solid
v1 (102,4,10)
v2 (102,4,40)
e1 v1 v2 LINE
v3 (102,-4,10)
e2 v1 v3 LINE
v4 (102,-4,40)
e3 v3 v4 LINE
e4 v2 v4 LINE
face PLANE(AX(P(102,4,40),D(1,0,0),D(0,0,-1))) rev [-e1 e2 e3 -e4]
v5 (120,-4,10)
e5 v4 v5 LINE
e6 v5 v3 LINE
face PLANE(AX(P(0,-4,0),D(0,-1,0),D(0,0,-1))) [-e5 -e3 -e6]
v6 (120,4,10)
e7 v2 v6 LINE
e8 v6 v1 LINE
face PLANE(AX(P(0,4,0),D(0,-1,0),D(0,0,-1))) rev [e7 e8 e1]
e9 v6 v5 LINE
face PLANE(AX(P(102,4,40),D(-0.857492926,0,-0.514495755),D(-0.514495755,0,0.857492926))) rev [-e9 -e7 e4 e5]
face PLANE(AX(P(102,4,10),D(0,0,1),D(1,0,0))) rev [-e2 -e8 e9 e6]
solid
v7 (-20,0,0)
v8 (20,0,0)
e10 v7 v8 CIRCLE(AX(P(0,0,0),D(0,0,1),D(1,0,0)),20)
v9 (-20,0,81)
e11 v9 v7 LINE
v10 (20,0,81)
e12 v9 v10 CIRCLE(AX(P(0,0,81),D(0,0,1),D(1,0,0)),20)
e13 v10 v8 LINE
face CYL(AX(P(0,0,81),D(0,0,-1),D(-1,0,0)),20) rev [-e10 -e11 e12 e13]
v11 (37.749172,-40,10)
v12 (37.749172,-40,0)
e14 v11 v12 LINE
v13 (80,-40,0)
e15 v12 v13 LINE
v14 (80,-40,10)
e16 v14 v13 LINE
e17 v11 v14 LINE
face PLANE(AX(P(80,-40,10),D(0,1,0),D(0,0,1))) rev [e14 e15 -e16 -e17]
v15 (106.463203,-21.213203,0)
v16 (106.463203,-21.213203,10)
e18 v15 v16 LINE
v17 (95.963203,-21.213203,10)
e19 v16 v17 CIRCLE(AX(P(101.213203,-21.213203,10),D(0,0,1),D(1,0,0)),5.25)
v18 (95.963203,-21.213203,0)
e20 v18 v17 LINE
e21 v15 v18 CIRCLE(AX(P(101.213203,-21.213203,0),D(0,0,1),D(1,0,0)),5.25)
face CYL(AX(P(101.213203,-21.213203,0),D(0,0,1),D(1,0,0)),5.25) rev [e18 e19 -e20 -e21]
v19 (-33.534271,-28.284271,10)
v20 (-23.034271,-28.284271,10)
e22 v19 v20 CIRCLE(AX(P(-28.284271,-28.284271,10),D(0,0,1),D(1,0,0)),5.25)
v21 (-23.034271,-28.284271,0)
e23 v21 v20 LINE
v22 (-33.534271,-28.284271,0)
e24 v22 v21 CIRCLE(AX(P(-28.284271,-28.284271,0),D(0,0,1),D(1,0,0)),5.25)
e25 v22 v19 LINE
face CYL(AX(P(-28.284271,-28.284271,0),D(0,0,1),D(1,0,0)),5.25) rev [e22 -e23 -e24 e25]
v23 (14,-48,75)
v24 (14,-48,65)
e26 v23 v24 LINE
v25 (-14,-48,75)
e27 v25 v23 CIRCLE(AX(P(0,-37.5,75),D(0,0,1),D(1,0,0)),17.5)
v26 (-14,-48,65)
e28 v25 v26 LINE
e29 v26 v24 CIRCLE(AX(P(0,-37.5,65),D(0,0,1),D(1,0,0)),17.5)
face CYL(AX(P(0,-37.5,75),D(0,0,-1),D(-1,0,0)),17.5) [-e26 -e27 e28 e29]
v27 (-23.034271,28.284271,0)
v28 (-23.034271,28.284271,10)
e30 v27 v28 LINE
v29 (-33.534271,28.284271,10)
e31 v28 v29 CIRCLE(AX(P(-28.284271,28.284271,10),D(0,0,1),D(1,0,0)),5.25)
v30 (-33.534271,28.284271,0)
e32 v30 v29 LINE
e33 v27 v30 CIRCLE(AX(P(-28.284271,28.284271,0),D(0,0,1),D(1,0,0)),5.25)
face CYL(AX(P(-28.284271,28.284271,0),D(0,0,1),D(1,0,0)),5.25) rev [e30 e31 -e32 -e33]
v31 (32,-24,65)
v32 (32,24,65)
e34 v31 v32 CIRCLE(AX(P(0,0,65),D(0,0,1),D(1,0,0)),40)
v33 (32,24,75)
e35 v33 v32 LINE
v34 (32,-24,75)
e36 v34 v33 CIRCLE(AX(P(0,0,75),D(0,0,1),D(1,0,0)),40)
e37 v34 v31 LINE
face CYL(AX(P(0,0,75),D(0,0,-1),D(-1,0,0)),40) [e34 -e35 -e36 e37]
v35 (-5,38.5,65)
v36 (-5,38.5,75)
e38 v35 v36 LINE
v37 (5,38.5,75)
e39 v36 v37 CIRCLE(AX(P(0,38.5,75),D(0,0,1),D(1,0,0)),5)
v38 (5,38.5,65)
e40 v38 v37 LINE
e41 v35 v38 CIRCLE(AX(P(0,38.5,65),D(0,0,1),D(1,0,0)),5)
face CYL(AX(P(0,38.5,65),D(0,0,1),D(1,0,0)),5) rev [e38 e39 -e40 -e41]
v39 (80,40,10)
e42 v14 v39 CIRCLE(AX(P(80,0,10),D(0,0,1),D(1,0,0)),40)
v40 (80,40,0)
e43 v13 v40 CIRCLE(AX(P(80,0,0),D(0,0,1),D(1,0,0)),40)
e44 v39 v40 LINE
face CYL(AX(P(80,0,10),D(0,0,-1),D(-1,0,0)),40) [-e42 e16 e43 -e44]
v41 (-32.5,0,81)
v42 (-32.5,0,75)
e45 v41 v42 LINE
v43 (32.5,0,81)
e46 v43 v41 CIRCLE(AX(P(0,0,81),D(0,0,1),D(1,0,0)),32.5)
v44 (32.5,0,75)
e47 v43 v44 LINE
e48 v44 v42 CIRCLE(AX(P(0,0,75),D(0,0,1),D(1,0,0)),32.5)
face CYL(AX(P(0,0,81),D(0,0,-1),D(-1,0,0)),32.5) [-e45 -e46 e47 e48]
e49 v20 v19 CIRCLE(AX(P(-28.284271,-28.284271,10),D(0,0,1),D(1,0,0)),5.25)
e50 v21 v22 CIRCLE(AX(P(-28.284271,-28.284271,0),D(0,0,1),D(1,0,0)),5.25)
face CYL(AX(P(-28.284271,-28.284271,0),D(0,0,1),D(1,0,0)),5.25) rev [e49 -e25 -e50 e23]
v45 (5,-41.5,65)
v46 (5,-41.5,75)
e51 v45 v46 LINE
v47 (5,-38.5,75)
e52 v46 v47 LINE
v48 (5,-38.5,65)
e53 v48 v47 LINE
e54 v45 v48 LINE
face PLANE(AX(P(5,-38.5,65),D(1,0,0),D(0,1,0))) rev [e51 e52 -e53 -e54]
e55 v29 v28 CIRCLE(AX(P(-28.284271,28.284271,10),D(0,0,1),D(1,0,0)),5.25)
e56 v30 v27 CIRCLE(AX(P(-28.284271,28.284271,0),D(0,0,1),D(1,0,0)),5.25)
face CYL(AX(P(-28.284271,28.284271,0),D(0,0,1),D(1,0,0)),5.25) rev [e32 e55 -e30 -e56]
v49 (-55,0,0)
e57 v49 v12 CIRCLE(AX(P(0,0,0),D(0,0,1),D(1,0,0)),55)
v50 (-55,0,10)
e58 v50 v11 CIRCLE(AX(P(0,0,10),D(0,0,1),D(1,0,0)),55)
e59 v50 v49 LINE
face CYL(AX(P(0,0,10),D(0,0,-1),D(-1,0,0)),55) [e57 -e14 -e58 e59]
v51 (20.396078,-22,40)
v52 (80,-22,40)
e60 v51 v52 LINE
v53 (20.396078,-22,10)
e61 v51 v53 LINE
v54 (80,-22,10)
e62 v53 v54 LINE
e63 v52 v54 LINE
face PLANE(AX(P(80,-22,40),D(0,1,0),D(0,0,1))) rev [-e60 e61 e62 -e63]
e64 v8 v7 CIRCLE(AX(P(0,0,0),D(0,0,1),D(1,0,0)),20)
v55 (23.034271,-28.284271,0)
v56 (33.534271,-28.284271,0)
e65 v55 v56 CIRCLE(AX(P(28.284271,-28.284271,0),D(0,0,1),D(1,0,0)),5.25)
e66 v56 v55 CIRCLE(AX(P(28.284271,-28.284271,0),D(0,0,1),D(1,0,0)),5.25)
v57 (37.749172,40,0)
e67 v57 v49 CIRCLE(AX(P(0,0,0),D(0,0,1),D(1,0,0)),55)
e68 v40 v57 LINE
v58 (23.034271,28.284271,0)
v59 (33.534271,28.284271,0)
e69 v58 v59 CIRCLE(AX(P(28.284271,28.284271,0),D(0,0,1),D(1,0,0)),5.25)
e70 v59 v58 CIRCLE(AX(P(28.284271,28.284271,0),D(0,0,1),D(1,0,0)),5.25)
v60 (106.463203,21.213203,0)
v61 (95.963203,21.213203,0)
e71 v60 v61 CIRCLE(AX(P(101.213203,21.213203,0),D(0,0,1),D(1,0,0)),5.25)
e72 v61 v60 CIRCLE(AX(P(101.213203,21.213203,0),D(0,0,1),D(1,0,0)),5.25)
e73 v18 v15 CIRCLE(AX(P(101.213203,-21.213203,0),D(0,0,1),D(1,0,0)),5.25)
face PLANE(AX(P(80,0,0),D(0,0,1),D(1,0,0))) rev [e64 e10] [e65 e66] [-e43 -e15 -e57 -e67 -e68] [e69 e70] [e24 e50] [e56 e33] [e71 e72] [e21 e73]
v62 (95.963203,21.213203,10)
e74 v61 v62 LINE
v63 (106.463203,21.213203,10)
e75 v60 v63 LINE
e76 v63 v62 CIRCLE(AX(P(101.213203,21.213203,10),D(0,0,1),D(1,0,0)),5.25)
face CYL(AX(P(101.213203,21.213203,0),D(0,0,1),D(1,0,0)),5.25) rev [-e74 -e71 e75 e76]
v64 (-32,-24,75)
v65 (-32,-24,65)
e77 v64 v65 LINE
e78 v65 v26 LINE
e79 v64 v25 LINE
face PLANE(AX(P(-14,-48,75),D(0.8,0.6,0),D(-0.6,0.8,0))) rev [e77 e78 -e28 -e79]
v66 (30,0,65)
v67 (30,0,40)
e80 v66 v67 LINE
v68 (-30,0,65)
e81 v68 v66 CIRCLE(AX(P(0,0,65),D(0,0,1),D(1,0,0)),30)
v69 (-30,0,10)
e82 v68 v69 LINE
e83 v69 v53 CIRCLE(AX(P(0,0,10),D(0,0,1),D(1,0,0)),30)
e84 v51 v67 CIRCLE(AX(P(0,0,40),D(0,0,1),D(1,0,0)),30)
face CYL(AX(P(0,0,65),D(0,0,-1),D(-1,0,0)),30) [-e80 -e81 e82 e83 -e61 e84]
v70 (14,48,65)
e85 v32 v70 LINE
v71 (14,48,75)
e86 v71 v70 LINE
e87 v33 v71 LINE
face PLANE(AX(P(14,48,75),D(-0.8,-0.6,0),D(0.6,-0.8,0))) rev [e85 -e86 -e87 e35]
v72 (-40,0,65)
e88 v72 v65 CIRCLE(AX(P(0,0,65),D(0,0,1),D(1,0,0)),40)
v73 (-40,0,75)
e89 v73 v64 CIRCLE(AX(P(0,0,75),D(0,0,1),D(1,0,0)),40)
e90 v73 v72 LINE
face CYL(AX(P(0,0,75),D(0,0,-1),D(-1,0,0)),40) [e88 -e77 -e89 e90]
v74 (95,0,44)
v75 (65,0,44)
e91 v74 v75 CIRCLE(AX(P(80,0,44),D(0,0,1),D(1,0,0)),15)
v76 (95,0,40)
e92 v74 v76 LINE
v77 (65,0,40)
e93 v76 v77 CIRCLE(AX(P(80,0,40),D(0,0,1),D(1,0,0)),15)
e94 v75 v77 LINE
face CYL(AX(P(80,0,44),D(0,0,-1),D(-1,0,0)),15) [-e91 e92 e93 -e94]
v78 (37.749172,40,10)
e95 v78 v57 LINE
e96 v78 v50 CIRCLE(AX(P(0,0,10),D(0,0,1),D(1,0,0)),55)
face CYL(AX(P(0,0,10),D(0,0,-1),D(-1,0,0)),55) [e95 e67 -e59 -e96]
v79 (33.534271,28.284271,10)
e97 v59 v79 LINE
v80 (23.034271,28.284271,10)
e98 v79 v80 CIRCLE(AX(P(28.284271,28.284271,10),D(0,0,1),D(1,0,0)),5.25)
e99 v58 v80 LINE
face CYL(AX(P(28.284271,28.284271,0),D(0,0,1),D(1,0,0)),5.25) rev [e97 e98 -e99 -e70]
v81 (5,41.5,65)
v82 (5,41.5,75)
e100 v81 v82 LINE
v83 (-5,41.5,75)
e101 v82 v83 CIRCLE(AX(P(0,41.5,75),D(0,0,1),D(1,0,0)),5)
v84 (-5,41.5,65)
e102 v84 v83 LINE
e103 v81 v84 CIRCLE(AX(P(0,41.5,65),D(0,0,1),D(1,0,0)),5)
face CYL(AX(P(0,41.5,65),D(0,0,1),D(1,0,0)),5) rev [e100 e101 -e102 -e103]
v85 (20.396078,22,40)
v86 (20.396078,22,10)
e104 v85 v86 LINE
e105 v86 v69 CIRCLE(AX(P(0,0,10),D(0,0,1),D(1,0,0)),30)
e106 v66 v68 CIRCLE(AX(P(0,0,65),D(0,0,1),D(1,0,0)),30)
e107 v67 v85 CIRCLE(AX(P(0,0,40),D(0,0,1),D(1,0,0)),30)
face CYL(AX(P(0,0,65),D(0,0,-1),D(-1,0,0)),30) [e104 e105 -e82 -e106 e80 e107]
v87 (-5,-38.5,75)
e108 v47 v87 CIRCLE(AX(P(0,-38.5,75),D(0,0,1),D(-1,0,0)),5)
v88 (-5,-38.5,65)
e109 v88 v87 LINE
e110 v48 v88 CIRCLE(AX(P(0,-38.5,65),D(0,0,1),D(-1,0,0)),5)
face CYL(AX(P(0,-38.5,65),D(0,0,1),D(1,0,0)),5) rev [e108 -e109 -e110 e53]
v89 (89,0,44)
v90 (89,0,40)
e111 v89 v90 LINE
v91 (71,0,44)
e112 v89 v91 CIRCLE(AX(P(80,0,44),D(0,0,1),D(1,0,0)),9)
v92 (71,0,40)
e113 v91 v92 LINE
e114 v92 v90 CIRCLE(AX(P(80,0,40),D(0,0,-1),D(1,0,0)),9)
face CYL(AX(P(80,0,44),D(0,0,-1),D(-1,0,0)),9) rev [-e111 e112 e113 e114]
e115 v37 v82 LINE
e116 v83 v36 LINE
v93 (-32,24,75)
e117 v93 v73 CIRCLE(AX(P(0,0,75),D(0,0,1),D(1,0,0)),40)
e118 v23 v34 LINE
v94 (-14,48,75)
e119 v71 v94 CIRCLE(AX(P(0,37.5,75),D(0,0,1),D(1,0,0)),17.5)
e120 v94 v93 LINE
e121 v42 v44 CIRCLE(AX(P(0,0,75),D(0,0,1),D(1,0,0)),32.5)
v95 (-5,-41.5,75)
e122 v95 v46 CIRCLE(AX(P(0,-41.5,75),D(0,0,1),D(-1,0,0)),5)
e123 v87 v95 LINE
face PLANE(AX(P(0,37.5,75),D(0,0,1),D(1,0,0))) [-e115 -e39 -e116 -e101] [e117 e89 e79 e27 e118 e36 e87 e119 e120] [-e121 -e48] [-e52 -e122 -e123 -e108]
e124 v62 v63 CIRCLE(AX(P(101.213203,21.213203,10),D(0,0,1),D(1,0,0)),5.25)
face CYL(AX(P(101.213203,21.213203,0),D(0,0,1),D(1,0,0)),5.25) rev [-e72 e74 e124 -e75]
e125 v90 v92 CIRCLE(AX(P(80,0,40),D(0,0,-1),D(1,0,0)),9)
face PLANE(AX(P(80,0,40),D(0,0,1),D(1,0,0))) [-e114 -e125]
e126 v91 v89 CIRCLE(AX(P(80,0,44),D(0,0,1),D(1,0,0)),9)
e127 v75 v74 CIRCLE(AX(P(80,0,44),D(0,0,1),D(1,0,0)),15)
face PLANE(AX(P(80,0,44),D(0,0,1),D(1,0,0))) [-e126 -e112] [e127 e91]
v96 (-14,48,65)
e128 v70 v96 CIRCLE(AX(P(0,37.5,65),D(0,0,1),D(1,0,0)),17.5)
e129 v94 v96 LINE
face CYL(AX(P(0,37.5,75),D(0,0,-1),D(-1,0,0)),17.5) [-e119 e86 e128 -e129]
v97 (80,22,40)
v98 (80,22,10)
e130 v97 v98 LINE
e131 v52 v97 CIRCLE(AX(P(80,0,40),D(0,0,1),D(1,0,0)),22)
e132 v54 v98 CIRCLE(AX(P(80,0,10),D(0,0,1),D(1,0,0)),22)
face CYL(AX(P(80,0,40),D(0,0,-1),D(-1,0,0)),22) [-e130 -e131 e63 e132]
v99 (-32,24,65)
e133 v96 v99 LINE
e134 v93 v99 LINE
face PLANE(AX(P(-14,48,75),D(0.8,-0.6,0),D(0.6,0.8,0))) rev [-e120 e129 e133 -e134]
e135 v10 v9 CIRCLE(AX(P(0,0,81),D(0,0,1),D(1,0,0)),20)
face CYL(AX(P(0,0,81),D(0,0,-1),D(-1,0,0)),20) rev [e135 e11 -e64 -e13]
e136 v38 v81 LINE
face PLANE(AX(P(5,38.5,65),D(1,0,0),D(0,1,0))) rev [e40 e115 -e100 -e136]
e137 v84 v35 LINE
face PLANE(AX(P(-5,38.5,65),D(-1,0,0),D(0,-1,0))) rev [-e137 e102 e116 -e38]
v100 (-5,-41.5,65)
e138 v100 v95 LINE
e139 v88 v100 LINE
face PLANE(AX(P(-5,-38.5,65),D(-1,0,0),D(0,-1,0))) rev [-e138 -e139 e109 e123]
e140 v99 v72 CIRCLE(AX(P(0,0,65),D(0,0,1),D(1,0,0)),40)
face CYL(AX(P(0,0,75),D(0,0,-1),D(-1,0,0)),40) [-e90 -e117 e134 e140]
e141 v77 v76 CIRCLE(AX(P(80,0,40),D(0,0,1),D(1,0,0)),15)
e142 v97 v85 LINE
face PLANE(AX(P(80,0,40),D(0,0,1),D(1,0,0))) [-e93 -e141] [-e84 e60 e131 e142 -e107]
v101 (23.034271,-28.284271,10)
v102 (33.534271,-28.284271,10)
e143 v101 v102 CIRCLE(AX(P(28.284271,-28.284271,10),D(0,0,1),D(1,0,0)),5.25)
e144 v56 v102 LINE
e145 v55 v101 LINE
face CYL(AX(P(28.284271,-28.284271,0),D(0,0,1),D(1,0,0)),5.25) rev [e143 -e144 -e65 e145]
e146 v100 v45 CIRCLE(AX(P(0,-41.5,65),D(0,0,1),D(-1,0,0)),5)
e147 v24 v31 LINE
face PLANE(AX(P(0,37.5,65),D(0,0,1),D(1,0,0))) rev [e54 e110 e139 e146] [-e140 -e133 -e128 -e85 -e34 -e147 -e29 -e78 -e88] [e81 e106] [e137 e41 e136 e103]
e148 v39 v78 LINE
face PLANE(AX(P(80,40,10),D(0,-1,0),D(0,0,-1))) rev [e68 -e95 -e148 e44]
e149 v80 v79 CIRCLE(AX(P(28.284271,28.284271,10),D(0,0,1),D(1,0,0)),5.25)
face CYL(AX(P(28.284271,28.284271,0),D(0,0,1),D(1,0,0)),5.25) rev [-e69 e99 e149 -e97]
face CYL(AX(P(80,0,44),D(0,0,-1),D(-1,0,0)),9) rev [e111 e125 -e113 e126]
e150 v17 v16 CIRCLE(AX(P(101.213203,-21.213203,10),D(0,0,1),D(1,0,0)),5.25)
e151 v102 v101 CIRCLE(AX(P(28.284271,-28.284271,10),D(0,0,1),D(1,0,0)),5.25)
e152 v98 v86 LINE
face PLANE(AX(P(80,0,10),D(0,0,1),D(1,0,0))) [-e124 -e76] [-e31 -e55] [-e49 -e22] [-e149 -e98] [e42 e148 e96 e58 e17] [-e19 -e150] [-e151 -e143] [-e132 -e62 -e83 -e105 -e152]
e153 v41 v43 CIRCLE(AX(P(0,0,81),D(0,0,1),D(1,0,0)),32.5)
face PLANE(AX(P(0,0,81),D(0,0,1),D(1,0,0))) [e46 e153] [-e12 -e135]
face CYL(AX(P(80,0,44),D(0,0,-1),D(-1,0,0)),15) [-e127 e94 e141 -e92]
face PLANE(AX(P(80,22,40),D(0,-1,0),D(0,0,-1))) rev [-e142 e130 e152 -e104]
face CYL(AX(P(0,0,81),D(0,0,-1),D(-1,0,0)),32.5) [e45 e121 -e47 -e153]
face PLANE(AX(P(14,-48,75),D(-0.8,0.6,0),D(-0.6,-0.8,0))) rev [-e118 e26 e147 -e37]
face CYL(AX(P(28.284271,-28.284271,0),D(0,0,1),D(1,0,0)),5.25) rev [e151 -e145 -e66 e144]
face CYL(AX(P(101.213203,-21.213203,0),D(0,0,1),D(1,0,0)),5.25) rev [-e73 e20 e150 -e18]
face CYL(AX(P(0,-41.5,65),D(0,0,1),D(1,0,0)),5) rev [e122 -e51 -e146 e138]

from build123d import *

# Parameters (mm, degrees)
BASE_FLANGE_DEPTH                = 10
MAIN_BARREL_SKETCH_R             = 30
MAIN_BARREL_60_DEPTH             = 55
FLANGE_HOLES_SKETCH_R            = 5.25
FLANGE_HOLES_4X_10_5_PCD80_DEPTH = 144.003496461
FLANGE_SIDE_HOLES_SKETCH_R       = 5.25
FLANGE_SIDE_HOLES_10_5_DEPTH     = 144.003496461
SIDE_ARM_DEPTH                   = 30
ARM_BOSS_SKETCH_R                = 15
ARM_BOSS_SKETCH_R_2              = 9
ARM_BOSS_DEPTH                   = 4
GUSSET_RIB_DEPTH                 = 4
END_FLANGE_DEPTH                 = 10
SPIGOT_RING_SKETCH_R             = 32.5
SPIGOT_RING_SKETCH_R_2           = 20
SPIGOT_RING_65_DEPTH             = 6
THROUGH_BORE_SKETCH_R            = 20
THROUGH_BORE_DEPTH               = 152.822264507
FLANGE_SLOT_DEPTH                = 10
SLOT_AND_RING_PATTERN_2X_COUNT   = 2


with BuildPart() as part:
    # Base Flange Sketch → Base Flange (new body)
    with BuildSketch(Plane.XY):
        with BuildLine():
            Line((80, 40), (37.749172176, 40))
            ThreePointArc((37.749172176, 40), (-55, 0), (37.749172176, -40))
            Line((37.749172176, -40), (80, -40))
            ThreePointArc((80, -40), (120, 0), (80, 40))
        make_face()
    extrude(amount=BASE_FLANGE_DEPTH)

    # Main Barrel Sketch → Main Barrel Ø60 (add)
    with BuildSketch(Plane.XY.offset(10)):
        Circle(MAIN_BARREL_SKETCH_R)
    extrude(amount=MAIN_BARREL_60_DEPTH)

    # Flange Holes Sketch → Flange Holes 4xØ10.5 PCD80 (cut, through all)
    with BuildSketch(Plane.XY.offset(10)):
        with Locations((28.284271247, 28.284271247)):
            Circle(FLANGE_HOLES_SKETCH_R)
        with Locations((28.284271247, -28.284271247)):
            Circle(FLANGE_HOLES_SKETCH_R)
        with Locations((-28.284271247, -28.284271247)):
            Circle(FLANGE_HOLES_SKETCH_R)
        with Locations((-28.284271247, 28.284271247)):
            Circle(FLANGE_HOLES_SKETCH_R)
    extrude(amount=-FLANGE_HOLES_4X_10_5_PCD80_DEPTH, mode=Mode.SUBTRACT)

    # Flange Side Holes Sketch → Flange Side Holes Ø10.5 (cut, through all)
    with BuildSketch(Plane.XY.offset(10)):
        with Locations((101.213203436, 21.213203436)):
            Circle(FLANGE_SIDE_HOLES_SKETCH_R)
        with Locations((101.213203436, -21.213203436)):
            Circle(FLANGE_SIDE_HOLES_SKETCH_R)
    extrude(amount=-FLANGE_SIDE_HOLES_10_5_DEPTH, mode=Mode.SUBTRACT)

    # Side Arm Sketch → Side Arm (add)
    with BuildSketch(Plane.XY.offset(10)):
        with BuildLine():
            Line((80, 22), (20.396078054, 22))
            ThreePointArc((20.396078054, 22), (29.508776427, 0), (20.396078054, -22))
            Line((20.396078054, -22), (80, -22))
            ThreePointArc((80, -22), (102, 0), (80, 22))
        make_face()
    extrude(amount=SIDE_ARM_DEPTH)

    # Arm Boss Sketch → Arm Boss (add)
    with BuildSketch(Plane.XY.offset(40)):
        with Locations((80, 0)):
            Circle(ARM_BOSS_SKETCH_R)
        with Locations((80, 0)):
            Circle(ARM_BOSS_SKETCH_R_2, mode=Mode.SUBTRACT)
    extrude(amount=ARM_BOSS_DEPTH)

    # End Flange Sketch → End Flange (add)
    with BuildSketch(Plane.XY.offset(65)):
        with BuildLine():
            Line((14, 48), (32, 24))
            ThreePointArc((32, 24), (40, 0), (32, -24))
            Line((32, -24), (14, -48))
            ThreePointArc((14, -48), (0, -55), (-14, -48))
            Line((-14, -48), (-32, -24))
            ThreePointArc((-32, -24), (-40, 0), (-32, 24))
            Line((-32, 24), (-14, 48))
            ThreePointArc((-14, 48), (0, 55), (14, 48))
        make_face()
    extrude(amount=END_FLANGE_DEPTH)

    # Spigot Ring Sketch → Spigot Ring Ø65 (add)
    with BuildSketch(Plane.XY.offset(75)):
        Circle(SPIGOT_RING_SKETCH_R)
        Circle(SPIGOT_RING_SKETCH_R_2, mode=Mode.SUBTRACT)
    extrude(amount=SPIGOT_RING_65_DEPTH)

    # Through Bore Sketch → Through Bore (cut, through all)
    with BuildSketch(Plane.XY.offset(75)):
        Circle(THROUGH_BORE_SKETCH_R)
    extrude(amount=-THROUGH_BORE_DEPTH, mode=Mode.SUBTRACT)

    # Flange Slot Sketch → Flange Slot (cut)
    with BuildSketch(Plane.XY.offset(75)):
        with BuildLine():
            Line((-5, 38.5), (-5, 41.5))
            ThreePointArc((-5, 41.5), (0, 46.5), (5, 41.5))
            Line((5, 41.5), (5, 38.5))
            ThreePointArc((5, 38.5), (0, 33.5), (-5, 38.5))
        make_face()
    flange_slot = extrude(amount=-FLANGE_SLOT_DEPTH, mode=Mode.SUBTRACT)

    # Slot and Ring Pattern 2x: Flange Slot ×2 about axis
    slot_and_ring_pattern_2x_axis = Axis((0, 0, 0), (0, 0, 1))
    for i in range(1, SLOT_AND_RING_PATTERN_2X_COUNT):
        add(flange_slot.rotate(slot_and_ring_pattern_2x_axis, i * 360 / SLOT_AND_RING_PATTERN_2X_COUNT), mode=Mode.SUBTRACT)


with BuildPart() as body_2:
    # Gusset Rib Sketch → Gusset Rib (new, symmetric)
    with BuildSketch(Plane(origin=(0, 0, 0), x_dir=(1, 0, 0), z_dir=(0, 1, 0))):
        Polygon((102, -40), (120, -10), (102, -10), align=None)
    extrude(amount=GUSSET_RIB_DEPTH, both=True)


solid = Compound([part.part, body_2.part])
